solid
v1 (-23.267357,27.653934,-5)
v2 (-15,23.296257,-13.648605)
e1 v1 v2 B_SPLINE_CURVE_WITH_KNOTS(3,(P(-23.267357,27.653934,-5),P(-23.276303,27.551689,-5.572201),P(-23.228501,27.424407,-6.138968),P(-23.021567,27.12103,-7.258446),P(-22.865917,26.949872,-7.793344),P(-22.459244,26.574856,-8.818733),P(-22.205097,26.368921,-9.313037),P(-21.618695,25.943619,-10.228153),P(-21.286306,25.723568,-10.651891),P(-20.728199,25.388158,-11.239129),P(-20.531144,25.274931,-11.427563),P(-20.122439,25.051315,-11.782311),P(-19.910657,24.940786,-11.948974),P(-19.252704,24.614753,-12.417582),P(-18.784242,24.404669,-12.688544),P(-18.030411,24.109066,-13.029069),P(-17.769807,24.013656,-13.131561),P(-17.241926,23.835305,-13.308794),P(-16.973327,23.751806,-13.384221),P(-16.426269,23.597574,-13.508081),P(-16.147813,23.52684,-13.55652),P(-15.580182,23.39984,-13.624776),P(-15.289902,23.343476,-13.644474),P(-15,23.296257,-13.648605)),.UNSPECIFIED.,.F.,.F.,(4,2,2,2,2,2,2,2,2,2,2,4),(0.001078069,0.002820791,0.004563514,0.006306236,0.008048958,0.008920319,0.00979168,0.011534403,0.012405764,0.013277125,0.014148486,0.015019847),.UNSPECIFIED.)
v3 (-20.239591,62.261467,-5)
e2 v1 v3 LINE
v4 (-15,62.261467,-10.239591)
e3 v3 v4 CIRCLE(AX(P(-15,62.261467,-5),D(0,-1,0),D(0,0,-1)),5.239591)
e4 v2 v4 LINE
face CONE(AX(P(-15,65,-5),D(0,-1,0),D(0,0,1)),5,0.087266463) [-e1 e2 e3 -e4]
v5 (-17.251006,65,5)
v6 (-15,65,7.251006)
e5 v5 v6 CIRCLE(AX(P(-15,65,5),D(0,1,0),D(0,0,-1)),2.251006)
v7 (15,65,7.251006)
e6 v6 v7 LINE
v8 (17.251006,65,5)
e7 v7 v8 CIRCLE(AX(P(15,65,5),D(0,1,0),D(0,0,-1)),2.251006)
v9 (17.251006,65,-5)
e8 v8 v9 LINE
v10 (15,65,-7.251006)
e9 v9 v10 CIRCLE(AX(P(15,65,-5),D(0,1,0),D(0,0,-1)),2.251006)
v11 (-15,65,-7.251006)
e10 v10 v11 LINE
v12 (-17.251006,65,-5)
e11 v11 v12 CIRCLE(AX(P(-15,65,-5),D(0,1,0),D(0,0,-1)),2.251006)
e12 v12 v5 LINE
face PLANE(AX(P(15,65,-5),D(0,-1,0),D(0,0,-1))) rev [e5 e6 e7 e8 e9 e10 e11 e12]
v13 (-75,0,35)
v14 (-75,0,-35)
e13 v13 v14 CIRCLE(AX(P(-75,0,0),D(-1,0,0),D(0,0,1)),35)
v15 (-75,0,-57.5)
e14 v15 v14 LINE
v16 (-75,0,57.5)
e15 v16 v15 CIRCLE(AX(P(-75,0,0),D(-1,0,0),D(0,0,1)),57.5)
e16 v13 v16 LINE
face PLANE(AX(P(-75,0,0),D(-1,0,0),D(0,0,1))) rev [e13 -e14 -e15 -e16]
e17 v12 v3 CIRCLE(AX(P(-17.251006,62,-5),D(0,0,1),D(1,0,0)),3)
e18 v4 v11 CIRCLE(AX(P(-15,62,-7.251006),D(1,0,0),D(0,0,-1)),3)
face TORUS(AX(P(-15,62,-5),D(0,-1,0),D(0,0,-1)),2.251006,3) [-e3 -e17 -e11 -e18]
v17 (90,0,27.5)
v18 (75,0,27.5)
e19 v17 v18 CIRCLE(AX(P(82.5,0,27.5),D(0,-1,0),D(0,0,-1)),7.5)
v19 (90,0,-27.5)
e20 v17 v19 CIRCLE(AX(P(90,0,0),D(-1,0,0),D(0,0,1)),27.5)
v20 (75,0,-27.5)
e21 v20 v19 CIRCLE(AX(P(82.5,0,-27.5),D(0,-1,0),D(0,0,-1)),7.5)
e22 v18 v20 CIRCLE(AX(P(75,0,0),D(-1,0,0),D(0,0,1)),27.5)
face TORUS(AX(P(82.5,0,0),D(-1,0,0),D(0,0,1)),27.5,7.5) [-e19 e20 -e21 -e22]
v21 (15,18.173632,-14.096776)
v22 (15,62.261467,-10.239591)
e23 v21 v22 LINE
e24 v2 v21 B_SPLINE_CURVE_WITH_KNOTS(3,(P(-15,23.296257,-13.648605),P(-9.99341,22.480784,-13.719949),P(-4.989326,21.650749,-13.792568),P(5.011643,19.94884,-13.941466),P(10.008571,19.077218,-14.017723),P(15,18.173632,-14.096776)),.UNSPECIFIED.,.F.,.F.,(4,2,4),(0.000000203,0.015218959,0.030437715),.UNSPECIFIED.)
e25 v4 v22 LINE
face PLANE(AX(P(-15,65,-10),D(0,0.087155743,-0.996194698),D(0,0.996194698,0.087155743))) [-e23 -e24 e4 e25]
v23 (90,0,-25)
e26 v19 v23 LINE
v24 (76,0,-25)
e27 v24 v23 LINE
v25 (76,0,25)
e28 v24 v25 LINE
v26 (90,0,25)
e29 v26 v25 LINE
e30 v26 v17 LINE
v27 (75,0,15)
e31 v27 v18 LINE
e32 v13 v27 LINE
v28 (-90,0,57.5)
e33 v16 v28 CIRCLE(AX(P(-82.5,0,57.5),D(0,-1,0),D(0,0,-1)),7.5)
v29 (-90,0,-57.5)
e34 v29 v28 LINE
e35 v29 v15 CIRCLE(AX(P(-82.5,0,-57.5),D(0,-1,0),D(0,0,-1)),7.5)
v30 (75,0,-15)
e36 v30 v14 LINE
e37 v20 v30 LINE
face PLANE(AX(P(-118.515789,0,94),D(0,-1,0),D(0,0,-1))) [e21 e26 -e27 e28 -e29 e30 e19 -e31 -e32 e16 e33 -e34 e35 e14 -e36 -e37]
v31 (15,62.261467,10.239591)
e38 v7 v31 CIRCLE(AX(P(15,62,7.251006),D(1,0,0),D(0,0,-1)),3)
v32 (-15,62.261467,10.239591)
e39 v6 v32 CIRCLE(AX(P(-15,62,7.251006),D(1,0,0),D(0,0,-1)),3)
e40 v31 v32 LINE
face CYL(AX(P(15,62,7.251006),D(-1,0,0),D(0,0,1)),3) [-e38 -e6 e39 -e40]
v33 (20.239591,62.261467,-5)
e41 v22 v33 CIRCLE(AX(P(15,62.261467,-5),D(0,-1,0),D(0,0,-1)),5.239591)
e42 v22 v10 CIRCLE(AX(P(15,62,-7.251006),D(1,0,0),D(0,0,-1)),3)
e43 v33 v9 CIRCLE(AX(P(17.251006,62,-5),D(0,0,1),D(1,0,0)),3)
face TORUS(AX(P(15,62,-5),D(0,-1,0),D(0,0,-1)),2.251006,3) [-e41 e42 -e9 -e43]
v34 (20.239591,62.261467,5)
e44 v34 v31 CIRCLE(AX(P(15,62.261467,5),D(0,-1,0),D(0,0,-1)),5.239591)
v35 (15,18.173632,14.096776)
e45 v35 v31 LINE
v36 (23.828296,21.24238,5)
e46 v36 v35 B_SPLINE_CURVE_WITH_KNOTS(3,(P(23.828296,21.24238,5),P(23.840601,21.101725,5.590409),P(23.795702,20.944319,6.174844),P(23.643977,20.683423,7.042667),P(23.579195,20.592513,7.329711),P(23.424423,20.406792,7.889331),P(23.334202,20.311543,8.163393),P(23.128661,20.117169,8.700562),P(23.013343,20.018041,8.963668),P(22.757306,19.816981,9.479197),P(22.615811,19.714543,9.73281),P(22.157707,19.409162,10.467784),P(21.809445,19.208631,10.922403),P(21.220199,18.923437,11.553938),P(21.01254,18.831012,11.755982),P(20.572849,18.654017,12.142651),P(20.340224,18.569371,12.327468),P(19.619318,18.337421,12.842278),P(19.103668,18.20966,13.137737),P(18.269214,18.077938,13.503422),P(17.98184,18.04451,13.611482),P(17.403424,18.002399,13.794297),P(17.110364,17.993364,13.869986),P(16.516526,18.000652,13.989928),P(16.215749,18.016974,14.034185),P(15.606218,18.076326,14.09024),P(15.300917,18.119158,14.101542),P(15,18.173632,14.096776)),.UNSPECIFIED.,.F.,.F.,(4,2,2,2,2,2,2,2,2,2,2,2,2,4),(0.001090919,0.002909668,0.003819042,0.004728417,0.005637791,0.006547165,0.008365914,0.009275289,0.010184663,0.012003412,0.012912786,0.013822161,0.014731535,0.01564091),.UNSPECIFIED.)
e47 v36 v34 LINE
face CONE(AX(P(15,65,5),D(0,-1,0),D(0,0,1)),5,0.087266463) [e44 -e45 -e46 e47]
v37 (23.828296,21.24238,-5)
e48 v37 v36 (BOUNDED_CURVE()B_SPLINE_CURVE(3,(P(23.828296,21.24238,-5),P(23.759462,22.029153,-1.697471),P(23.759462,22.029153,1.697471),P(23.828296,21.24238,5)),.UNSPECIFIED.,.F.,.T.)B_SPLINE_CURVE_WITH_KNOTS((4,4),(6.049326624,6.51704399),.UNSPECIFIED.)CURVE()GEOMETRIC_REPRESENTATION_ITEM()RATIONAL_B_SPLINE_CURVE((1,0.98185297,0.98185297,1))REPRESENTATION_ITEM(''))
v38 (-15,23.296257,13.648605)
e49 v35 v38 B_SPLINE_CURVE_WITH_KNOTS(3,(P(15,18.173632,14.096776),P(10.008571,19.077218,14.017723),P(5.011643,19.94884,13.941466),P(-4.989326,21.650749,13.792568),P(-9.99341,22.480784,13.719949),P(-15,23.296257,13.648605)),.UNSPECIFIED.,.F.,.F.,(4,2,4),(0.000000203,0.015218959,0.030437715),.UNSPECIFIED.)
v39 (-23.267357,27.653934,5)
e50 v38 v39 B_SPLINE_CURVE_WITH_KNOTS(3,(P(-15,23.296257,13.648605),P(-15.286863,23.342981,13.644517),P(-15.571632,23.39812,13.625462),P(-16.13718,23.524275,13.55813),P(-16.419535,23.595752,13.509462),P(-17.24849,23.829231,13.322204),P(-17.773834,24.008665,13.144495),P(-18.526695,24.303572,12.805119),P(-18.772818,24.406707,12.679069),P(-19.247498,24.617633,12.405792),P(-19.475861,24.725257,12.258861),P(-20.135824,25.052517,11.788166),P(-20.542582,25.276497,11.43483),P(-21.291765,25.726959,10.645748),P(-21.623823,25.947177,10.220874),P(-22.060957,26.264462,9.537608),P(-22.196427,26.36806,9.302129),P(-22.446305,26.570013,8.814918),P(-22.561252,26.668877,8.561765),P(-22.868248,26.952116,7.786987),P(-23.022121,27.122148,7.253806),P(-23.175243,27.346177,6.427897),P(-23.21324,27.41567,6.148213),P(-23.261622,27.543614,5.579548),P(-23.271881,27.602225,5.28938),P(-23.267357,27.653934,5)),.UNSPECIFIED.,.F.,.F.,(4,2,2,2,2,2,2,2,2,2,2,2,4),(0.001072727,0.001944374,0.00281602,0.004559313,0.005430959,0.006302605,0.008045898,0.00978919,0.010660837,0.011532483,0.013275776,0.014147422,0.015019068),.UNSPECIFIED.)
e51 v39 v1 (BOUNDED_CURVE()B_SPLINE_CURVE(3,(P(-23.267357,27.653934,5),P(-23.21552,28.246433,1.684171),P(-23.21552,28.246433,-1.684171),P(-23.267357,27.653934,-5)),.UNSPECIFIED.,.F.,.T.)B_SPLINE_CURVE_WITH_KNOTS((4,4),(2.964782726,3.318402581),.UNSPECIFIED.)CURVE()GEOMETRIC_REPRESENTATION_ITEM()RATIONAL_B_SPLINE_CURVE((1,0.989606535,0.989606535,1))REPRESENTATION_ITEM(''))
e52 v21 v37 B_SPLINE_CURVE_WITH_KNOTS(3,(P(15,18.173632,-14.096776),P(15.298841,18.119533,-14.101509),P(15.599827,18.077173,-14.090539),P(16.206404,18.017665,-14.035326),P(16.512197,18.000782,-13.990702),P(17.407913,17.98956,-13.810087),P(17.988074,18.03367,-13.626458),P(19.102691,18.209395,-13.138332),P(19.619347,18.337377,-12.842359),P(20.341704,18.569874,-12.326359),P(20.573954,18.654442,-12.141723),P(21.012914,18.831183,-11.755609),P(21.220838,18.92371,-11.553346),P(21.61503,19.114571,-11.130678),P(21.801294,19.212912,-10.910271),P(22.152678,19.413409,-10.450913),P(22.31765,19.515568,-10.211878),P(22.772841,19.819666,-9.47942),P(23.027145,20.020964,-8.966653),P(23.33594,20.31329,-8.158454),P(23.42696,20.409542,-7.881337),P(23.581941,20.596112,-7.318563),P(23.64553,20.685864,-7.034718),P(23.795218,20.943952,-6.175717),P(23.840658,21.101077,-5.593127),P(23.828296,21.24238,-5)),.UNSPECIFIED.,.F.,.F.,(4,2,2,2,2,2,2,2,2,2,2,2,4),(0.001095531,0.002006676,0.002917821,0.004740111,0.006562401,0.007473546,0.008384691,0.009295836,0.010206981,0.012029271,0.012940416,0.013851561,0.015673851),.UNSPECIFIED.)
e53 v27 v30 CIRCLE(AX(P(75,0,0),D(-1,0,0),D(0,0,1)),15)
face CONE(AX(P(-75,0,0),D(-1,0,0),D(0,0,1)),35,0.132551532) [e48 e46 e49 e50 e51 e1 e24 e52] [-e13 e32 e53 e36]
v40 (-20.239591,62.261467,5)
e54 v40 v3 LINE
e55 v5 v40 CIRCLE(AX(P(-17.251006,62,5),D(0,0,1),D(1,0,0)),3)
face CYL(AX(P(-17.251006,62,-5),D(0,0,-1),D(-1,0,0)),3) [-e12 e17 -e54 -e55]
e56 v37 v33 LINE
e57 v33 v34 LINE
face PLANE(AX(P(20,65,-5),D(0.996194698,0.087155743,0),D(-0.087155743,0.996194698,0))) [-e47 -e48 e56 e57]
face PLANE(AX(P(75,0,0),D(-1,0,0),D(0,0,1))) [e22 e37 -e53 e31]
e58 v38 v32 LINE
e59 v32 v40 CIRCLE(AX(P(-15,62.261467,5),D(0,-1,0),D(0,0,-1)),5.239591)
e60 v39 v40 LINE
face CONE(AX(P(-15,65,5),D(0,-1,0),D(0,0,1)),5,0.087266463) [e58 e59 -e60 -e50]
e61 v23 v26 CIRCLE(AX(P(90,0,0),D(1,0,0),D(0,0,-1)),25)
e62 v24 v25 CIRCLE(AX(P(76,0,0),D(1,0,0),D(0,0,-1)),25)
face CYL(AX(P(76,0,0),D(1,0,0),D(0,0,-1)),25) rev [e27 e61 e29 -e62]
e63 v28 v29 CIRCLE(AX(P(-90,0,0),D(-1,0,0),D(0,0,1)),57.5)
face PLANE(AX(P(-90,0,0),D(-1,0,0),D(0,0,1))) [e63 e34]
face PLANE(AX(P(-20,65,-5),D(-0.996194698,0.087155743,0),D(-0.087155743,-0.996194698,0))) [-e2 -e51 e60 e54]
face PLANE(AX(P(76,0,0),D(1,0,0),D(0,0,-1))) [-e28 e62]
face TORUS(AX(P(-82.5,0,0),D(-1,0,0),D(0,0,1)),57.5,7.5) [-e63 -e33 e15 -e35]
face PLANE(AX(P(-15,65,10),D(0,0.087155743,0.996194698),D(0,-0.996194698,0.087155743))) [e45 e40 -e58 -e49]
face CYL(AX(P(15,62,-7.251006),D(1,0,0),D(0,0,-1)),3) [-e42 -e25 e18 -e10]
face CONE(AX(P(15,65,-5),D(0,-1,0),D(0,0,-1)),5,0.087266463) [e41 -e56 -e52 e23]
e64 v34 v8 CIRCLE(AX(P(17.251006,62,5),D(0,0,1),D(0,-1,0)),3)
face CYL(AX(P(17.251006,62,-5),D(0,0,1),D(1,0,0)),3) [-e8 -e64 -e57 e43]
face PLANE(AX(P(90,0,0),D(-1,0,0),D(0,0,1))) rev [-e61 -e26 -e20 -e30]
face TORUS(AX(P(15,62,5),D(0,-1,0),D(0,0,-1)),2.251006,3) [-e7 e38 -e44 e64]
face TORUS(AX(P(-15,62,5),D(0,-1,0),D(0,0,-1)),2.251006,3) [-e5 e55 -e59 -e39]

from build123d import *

# Parameters (mm, degrees)
HALF_SPLIT_CUT_DEPTH         = 94
HALF_SPLIT_CUT_DEPTH_BACK    = 80
HALF_SPLIT_CUT_SKETCH_W      = 233.621052632
HALF_SPLIT_CUT_SKETCH_H      = 71.905263158
GRIP_BOSS_DRAFTED_5DEG_DEPTH = 65
GRIP_BOSS_DRAFTED_5DEG_DRAFT = 5
GRIP_BOSS_FILLET_R3_R        = 3
HOOK_END_RECESS_SKETCH_50_R  = 25
HOOK_END_RECESS_50X14_DEPTH  = 14


with BuildPart() as part:
    # Hook Body Profile → Hook Body Revolve (revolve)
    with BuildSketch(Plane.XY, mode=Mode.PRIVATE) as hook_body_revolve_sk:
        with BuildLine():
            Line((-90, 0), (-75, 0))
            Line((-75, 0), (-75, 35))
            Line((-75, 35), (-75, 57.5))
            ThreePointArc((-75, 57.5), (-82.5, 65), (-90, 57.5))
            Line((-90, 57.5), (-90, 0))
        make_face()
        Polygon((-75, 0), (0, 0), (75, 0), (75, 15), (-75, 35), align=None)
        with BuildLine():
            Line((75, 15), (75, 0))
            Line((75, 0), (90, 0))
            Line((90, 0), (90, 27.5))
            ThreePointArc((90, 27.5), (82.5, 35), (75, 27.5))
            Line((75, 27.5), (75, 15))
        make_face()
    revolve(hook_body_revolve_sk.sketch.rotate(Axis((0, 0, 0), (1, 0, 0)), 90), axis=Axis((0, 0, 0), (1, 0, 0)))

    # Half Split Cut Sketch → Half Split Cut (cut, two sides: drawn at the far end of the back side and taken through both)
    with BuildSketch(Plane.XY.offset(-HALF_SPLIT_CUT_DEPTH_BACK)):
        with Locations((-1.705263158, -35.952631579)):
            Rectangle(HALF_SPLIT_CUT_SKETCH_W, HALF_SPLIT_CUT_SKETCH_H)
    extrude(amount=HALF_SPLIT_CUT_DEPTH + HALF_SPLIT_CUT_DEPTH_BACK, mode=Mode.SUBTRACT)


with BuildPart() as grip_boss_drafted_5deg_tool:
    # Grip Boss Sketch 40x20 → Grip Boss Drafted 5deg (with draft: the straight prism first)
    with BuildSketch(Plane(origin=(0, 65, 0), x_dir=(1, 0, 0), z_dir=(0, 1, 0))):
        with BuildLine():
            ThreePointArc((-15, 10), (-18.535533906, 8.535533906), (-20, 5))
            Line((-20, 5), (-20, -5))
            ThreePointArc((-20, -5), (-18.535533906, -8.535533906), (-15, -10))
            Line((-15, -10), (15, -10))
            ThreePointArc((15, -10), (18.535533906, -8.535533906), (20, -5))
            Line((20, -5), (20, 5))
            ThreePointArc((20, 5), (18.535533906, 8.535533906), (15, 10))
            Line((15, 10), (-15, 10))
        make_face()
    extrude(amount=-GRIP_BOSS_DRAFTED_5DEG_DEPTH)
    # Grip Boss Drafted 5deg: the draft: its side faces are tilted about the plane it starts from
    grip_boss_drafted_5deg_sides = [grip_boss_drafted_5deg_tool.faces().sort_by_distance(p)[0] for p in [
        (-18.535533906, 32.5, -8.535533906),
        (-20, 32.5, 0),
        (-18.535533906, 32.5, 8.535533906),
        (0, 32.5, 10),
        (18.535533906, 32.5, 8.535533906),
        (20, 32.5, 0),
        (18.535533906, 32.5, -8.535533906),
        (0, 32.5, -10),
    ]]
    draft(grip_boss_drafted_5deg_sides, Plane(origin=(0, 65, 0), x_dir=(1, 0, 0), z_dir=(0, 1, 0)), GRIP_BOSS_DRAFTED_5DEG_DRAFT)


with BuildPart() as part_1:
    add(part.part)

    # Grip Boss Drafted 5deg: add grip_boss_drafted_5deg_tool
    add(grip_boss_drafted_5deg_tool.part)

    # Grip Boss Fillet R3
    grip_boss_fillet_r3_edges = [part_1.edges().sort_by_distance(p)[0] for p in [
        (18.535533906, 65, -8.535533906),
        (0, 65, -10),
        (-18.535533906, 65, -8.535533906),
        (-20, 65, 0),
        (-18.535533906, 65, 8.535533906),
        (0, 65, 10),
        (18.535533906, 65, 8.535533906),
        (20, 65, 0),
    ]]
    fillet(grip_boss_fillet_r3_edges, radius=GRIP_BOSS_FILLET_R3_R)

    # Hook End Recess Sketch Ø50 → Hook End Recess Ø50x14 (cut)
    with BuildSketch(Plane(origin=(90, 0, 0), x_dir=(0, 0, -1), z_dir=(1, 0, 0))):
        Circle(HOOK_END_RECESS_SKETCH_50_R)
    extrude(amount=-HOOK_END_RECESS_50X14_DEPTH, mode=Mode.SUBTRACT)


solid = part_1.part
